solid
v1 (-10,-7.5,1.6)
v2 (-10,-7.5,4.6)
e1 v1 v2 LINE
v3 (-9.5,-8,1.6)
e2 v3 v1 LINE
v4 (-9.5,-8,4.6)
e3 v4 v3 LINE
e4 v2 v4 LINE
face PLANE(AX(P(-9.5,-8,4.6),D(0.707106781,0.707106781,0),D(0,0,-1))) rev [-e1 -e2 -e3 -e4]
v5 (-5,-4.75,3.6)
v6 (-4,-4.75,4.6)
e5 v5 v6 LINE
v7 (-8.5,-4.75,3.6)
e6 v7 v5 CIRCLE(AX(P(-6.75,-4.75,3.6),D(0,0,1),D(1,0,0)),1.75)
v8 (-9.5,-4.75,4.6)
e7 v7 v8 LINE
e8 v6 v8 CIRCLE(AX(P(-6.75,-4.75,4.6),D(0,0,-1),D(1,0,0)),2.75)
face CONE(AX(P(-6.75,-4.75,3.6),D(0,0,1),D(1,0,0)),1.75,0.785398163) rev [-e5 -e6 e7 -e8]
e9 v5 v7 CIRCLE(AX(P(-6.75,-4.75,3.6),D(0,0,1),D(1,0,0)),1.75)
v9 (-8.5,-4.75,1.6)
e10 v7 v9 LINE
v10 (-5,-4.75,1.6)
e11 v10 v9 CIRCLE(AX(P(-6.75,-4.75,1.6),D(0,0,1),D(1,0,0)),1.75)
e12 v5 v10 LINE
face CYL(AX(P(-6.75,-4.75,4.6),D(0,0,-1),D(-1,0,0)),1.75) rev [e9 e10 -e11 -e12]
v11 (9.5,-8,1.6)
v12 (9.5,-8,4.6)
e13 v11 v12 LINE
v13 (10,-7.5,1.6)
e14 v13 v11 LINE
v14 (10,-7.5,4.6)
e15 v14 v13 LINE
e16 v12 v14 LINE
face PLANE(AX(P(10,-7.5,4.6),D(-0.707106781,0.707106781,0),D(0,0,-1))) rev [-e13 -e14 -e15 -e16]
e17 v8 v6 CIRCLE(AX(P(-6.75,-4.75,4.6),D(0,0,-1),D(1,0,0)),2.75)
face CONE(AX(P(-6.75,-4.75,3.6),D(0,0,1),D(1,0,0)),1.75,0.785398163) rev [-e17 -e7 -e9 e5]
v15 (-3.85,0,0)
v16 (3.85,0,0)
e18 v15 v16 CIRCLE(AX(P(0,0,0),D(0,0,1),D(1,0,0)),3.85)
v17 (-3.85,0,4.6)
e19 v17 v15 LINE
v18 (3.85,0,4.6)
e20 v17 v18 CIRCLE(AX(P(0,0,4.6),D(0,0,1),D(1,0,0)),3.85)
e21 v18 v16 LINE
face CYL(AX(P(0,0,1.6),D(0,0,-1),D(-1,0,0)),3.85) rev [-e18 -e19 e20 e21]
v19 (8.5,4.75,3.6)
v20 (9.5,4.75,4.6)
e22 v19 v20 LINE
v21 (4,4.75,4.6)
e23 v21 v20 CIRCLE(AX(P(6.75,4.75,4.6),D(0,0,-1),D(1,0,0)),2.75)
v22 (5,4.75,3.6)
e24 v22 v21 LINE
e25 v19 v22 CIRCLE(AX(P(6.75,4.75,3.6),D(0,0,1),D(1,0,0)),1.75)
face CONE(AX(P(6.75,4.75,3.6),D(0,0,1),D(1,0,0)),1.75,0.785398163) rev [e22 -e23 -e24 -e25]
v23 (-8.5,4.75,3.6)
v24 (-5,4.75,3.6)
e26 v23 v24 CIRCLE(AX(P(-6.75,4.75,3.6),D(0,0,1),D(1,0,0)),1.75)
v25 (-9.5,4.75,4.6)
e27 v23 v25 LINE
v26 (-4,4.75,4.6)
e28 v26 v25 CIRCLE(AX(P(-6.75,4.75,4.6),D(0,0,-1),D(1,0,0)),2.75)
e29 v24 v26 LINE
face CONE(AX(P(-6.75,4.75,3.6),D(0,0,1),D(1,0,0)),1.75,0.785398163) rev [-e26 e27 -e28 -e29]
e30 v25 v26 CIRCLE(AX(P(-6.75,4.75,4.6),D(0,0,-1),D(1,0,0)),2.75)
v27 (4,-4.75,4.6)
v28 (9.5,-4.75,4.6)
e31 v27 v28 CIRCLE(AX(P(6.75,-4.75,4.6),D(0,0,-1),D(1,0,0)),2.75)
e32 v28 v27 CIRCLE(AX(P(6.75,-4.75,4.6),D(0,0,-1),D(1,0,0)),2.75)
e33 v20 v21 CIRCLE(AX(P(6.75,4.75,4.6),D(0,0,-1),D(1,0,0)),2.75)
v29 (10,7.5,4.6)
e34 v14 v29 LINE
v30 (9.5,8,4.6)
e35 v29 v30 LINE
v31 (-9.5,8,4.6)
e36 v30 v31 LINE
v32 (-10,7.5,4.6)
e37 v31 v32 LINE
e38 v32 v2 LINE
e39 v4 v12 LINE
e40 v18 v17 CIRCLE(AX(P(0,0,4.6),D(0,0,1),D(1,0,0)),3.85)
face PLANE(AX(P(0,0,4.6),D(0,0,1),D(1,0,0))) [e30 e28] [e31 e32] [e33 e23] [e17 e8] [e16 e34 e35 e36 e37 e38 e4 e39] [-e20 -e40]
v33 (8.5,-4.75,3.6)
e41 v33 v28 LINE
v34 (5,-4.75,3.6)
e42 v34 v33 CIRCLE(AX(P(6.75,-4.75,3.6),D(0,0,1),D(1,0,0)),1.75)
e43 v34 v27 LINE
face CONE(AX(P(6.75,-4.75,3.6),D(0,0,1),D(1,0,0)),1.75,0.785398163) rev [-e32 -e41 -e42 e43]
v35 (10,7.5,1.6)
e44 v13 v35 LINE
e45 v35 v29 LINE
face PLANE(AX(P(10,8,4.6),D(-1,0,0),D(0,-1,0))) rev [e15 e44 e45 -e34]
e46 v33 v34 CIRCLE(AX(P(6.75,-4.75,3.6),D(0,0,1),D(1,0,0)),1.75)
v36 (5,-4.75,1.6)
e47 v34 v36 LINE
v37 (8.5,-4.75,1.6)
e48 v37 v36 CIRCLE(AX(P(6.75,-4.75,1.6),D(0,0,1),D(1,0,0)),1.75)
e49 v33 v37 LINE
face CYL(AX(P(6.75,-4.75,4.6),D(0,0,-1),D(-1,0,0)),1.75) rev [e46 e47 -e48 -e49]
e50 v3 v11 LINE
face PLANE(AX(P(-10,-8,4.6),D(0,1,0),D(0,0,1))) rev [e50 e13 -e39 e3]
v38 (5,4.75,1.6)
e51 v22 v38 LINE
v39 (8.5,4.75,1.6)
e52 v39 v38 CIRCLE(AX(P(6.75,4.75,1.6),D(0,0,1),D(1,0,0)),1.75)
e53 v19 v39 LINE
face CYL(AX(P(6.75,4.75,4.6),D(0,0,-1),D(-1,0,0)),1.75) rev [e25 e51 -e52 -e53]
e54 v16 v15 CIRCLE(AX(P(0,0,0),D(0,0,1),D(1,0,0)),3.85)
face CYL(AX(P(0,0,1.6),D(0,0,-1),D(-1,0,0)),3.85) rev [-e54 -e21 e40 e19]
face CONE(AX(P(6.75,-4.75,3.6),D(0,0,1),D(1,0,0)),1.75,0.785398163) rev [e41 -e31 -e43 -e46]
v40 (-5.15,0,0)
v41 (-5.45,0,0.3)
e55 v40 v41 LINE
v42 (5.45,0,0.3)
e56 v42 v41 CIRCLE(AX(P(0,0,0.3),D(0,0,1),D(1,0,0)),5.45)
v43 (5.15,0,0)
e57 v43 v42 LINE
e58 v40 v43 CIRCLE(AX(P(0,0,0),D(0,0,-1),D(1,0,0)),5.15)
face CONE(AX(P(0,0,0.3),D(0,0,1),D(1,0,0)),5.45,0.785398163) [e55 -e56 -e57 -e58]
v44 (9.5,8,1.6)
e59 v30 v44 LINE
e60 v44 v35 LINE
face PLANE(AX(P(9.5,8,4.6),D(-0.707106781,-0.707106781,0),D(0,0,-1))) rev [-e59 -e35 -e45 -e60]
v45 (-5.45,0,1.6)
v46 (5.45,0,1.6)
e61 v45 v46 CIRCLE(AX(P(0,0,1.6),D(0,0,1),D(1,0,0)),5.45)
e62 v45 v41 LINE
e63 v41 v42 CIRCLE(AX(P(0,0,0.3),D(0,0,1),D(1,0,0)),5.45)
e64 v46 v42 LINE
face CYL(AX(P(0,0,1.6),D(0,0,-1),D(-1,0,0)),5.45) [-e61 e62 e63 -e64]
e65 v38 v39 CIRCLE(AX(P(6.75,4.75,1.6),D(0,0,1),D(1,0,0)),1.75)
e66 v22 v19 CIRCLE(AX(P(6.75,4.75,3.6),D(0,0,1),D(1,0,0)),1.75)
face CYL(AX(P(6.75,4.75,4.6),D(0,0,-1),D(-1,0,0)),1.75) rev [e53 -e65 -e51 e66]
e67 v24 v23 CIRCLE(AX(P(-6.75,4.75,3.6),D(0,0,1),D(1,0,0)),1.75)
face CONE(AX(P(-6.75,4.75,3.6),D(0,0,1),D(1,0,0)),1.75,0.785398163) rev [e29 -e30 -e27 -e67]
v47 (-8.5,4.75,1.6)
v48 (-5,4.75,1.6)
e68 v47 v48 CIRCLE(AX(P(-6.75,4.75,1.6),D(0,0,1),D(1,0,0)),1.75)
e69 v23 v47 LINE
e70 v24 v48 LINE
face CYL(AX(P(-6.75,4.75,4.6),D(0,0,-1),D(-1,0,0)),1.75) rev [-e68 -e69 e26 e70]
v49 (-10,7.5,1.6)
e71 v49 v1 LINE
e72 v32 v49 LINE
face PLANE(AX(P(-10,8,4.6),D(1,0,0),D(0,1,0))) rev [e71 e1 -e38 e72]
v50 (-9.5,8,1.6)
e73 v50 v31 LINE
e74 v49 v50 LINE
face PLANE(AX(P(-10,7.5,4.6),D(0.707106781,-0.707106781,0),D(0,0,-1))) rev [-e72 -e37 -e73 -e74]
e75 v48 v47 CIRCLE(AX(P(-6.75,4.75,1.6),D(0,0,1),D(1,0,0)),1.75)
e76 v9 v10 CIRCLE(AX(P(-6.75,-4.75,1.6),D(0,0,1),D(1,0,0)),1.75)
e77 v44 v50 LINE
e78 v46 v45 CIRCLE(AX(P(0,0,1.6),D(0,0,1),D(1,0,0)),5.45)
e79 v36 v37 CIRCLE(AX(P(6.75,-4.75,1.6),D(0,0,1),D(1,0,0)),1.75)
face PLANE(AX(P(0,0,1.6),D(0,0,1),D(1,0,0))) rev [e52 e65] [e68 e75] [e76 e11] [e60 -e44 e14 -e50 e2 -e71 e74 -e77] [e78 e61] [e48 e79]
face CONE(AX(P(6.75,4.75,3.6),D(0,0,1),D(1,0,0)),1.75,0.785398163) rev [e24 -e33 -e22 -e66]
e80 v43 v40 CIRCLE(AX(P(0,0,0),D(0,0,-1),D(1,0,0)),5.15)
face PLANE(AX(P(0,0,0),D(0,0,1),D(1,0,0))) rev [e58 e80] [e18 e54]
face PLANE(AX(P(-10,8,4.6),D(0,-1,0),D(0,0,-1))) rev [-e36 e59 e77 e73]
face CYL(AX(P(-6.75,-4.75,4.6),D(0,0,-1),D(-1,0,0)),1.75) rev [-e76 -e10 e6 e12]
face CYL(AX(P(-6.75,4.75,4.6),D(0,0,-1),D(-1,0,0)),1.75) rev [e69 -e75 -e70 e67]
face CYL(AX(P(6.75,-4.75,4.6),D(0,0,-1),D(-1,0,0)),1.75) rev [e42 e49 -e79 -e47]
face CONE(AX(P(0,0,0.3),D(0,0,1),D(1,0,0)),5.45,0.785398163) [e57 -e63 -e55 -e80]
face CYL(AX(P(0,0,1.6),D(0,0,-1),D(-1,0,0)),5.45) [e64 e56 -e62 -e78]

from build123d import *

# Parameters (mm, degrees)
SKETCH1_R           = 5.45
SKETCH1_R_2         = 3.85
BOSS_EXTRUDE1_DEPTH = 1.6
SKETCH2_W           = 20
SKETCH2_H           = 16
SKETCH2_R           = 3.85
SKETCH2_R_2         = 1.75
BOSS_EXTRUDE2_DEPTH = 3
CHAMFER1_SIZE       = 0.3
CHAMFER2_SIZE       = 1
CHAMFER3_SIZE       = 0.5


with BuildPart() as part:
    # Sketch1 → Boss-Extrude1 (new body)
    with BuildSketch(Plane.XY):
        Circle(SKETCH1_R)
        Circle(SKETCH1_R_2, mode=Mode.SUBTRACT)
    extrude(amount=BOSS_EXTRUDE1_DEPTH)

    # Sketch2 → Boss-Extrude2 (add)
    with BuildSketch(Plane.XY.offset(1.6)):
        Rectangle(SKETCH2_W, SKETCH2_H)
        Circle(SKETCH2_R, mode=Mode.SUBTRACT)
        with Locations((-6.75, 4.75)):
            Circle(SKETCH2_R_2, mode=Mode.SUBTRACT)
        with Locations((-6.75, -4.75)):
            Circle(SKETCH2_R_2, mode=Mode.SUBTRACT)
        with Locations((6.75, -4.75)):
            Circle(SKETCH2_R_2, mode=Mode.SUBTRACT)
        with Locations((6.75, 4.75)):
            Circle(SKETCH2_R_2, mode=Mode.SUBTRACT)
    extrude(amount=BOSS_EXTRUDE2_DEPTH)

    # Chamfer1
    chamfer1_edges = [part.edges().sort_by_distance(p)[0] for p in [
        (-5.45, 0, 0),
    ]]
    chamfer(chamfer1_edges, length=CHAMFER1_SIZE)

    # Chamfer2
    chamfer2_edges = [part.edges().sort_by_distance(p)[0] for p in [
        (-8.5, 4.75, 4.6),
        (-8.5, -4.75, 4.6),
        (5, -4.75, 4.6),
        (5, 4.75, 4.6),
    ]]
    chamfer(chamfer2_edges, length=CHAMFER2_SIZE)

    # Chamfer3
    chamfer3_edges = [part.edges().sort_by_distance(p)[0] for p in [
        (10, -8, 3.1),
        (10, 8, 3.1),
        (-10, 8, 3.1),
        (-10, -8, 3.1),
    ]]
    chamfer(chamfer3_edges, length=CHAMFER3_SIZE)


solid = part.part
